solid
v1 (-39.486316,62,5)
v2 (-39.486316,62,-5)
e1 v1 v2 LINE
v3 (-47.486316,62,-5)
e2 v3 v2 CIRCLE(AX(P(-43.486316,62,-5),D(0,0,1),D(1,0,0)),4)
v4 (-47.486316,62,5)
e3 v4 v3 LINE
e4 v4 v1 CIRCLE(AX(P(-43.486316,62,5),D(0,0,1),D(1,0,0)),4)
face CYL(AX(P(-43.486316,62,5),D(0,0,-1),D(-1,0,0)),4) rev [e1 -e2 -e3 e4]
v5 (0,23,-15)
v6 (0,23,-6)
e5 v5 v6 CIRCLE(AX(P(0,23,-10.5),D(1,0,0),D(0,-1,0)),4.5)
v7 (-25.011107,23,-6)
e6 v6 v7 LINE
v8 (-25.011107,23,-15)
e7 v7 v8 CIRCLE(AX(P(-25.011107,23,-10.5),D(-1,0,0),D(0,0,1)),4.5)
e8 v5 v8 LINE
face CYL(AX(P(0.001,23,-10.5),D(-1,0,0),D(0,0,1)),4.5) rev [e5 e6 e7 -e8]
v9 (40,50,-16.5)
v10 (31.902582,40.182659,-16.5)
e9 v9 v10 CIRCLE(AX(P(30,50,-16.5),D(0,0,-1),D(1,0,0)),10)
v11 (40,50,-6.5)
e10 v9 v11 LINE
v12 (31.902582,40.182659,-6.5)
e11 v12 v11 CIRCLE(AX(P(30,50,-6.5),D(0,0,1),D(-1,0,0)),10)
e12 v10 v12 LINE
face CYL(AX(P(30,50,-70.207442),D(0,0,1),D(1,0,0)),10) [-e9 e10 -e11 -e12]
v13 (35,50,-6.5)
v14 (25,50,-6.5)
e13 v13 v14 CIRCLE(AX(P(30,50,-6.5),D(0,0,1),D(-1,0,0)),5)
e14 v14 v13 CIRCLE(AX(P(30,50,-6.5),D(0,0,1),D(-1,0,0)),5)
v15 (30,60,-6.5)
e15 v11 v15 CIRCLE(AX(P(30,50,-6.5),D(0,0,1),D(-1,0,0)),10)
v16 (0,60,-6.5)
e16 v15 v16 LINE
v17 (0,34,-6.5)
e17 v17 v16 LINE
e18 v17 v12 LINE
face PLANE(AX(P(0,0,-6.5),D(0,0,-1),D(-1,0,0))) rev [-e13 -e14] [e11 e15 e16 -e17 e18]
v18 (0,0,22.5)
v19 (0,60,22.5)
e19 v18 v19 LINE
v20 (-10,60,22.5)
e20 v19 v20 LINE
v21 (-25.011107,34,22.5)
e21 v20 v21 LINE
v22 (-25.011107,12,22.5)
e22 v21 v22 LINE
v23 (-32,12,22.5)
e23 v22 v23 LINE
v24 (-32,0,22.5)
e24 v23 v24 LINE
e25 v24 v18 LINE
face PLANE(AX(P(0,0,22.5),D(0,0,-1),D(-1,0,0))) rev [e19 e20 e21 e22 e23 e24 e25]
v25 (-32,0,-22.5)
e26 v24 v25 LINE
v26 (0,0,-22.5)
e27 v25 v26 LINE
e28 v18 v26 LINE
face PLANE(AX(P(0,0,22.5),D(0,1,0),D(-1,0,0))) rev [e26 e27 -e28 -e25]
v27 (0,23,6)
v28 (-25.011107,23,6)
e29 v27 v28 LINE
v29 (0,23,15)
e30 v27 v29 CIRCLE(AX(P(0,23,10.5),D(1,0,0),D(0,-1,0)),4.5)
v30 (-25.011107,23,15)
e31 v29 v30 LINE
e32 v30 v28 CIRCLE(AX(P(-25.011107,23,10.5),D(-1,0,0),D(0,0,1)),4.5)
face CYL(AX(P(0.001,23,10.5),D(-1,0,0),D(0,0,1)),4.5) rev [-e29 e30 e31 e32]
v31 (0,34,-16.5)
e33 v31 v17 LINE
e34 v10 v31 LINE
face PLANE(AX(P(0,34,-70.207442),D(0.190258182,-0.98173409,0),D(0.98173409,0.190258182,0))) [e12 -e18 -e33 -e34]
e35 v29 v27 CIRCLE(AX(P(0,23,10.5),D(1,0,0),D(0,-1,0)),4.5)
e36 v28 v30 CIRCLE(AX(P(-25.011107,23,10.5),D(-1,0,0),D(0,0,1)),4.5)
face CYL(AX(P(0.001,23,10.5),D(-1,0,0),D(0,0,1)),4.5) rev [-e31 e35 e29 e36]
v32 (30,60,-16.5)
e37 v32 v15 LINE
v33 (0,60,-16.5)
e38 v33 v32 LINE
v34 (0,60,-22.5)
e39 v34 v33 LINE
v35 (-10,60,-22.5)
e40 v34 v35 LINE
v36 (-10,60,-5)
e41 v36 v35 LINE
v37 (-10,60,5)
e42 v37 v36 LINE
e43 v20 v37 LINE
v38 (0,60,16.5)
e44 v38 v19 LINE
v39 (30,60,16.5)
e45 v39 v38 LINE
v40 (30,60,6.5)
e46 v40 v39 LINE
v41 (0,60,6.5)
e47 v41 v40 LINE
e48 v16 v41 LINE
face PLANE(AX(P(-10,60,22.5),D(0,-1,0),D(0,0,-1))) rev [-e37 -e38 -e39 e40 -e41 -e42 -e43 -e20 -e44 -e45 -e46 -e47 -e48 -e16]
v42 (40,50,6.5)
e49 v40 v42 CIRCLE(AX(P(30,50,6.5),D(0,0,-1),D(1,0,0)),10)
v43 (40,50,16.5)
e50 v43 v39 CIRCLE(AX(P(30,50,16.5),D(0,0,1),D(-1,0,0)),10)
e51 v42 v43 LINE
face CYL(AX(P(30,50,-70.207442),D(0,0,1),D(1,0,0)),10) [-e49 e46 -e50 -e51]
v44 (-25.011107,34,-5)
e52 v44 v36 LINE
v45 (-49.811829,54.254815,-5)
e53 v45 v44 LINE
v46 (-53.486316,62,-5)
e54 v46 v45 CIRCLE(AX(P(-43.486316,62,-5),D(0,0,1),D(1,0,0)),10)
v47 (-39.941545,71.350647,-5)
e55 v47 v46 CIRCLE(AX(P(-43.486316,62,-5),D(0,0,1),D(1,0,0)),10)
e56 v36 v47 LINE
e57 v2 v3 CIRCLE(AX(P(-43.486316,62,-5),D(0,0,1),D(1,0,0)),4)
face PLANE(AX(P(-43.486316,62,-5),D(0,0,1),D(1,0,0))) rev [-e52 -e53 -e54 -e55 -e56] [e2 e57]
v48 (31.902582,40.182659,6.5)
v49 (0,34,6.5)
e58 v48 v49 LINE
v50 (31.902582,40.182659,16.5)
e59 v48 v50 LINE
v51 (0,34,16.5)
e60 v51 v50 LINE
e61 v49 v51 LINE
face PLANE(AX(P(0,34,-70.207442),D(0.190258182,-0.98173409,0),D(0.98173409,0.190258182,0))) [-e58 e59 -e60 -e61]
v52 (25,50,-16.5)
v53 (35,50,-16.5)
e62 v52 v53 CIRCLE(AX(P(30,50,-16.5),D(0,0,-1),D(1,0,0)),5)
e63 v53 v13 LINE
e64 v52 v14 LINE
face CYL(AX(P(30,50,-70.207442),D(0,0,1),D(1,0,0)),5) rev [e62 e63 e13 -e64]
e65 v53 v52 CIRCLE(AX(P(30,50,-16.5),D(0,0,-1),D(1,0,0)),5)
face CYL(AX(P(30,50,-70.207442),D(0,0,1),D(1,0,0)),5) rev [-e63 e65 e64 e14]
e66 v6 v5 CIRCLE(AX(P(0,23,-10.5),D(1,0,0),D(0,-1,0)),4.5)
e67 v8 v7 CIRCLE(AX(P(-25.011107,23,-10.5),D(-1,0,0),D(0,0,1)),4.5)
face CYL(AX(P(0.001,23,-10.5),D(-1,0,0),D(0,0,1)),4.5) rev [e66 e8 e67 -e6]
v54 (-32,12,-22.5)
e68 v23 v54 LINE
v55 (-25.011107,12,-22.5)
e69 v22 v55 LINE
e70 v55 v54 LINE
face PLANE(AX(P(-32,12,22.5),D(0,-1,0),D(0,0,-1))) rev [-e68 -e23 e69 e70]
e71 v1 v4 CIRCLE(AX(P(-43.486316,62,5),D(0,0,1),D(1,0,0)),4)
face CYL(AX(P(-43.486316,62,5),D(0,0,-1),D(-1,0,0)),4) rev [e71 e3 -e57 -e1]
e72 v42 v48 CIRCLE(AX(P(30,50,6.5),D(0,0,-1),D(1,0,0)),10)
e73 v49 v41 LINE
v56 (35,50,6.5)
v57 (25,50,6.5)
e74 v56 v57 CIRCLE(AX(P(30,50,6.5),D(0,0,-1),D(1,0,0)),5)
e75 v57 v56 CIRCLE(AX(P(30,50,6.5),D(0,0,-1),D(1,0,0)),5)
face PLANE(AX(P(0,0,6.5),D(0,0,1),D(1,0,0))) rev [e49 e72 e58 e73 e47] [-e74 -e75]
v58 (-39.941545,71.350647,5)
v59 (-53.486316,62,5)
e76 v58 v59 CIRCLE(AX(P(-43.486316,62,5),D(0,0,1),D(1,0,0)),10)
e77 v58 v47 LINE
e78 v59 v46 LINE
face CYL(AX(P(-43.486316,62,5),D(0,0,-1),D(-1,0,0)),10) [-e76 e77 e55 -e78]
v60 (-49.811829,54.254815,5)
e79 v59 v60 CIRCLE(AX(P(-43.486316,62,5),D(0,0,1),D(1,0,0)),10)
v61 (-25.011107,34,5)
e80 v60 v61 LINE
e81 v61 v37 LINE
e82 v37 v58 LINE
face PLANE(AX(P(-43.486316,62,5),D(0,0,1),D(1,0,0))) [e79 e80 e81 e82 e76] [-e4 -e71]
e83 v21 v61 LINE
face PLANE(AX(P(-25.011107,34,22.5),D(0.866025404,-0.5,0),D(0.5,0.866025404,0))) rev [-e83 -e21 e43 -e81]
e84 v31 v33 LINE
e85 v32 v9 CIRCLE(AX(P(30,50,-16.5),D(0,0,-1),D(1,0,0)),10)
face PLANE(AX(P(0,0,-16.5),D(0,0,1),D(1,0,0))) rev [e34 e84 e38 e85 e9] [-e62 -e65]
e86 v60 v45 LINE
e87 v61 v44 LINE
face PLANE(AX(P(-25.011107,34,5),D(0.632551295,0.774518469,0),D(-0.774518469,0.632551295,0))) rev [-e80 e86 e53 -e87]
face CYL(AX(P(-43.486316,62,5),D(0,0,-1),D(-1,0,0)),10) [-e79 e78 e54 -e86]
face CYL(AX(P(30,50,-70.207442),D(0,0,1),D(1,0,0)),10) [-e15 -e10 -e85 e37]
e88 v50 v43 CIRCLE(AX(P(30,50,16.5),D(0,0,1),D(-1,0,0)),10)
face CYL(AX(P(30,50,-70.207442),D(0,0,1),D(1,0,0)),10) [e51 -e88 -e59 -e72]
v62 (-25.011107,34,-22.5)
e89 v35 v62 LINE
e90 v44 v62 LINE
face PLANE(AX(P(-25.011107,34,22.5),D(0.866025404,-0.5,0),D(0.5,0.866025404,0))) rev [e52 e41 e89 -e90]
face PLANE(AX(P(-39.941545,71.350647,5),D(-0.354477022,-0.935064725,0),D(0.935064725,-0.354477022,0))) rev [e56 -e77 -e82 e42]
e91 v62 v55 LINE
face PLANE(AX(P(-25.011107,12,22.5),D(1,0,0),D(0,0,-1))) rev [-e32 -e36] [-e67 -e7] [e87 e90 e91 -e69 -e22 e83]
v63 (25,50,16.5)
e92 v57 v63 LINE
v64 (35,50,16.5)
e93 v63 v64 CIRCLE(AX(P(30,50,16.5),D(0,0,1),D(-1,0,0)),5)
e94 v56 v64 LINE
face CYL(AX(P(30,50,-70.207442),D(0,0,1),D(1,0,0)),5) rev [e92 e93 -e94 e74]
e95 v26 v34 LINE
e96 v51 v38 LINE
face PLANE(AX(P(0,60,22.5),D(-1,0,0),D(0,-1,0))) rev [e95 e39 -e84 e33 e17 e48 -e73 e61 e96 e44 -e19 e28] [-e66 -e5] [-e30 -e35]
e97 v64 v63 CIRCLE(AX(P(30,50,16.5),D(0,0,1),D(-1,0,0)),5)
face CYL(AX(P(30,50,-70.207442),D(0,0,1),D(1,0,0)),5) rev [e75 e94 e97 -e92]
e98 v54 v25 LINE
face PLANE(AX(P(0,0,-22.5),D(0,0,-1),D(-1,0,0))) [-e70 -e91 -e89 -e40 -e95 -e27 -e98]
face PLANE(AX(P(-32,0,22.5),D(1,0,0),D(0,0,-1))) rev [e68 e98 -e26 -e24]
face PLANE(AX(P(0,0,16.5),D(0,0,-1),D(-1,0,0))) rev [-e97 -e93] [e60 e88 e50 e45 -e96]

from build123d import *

# Parameters (mm, degrees)
BASE_BLOCK_DEPTH           = 22.5
LUG_ARM_SKETCH_R           = 4
LUG_ARM_DEPTH              = 5
SIDE_HOLE_9_REACH          = 82.629
SIDE_HOLE_SKETCH_R         = 4.5
CLEVIS_FORK_SKETCH_R       = 5
CLEVIS_FORK_DEPTH          = 45
CLEVIS_PIN_HOLE_SKETCH_W   = 40
CLEVIS_PIN_HOLE_SKETCH_H   = 6
CLEVIS_PIN_HOLE_SKETCH_H_2 = 13
CLEVIS_PIN_HOLES_6_DEPTH   = 84.468772351


with BuildPart() as part:
    # Base Block Profile Sketch → Base Block (new, symmetric)
    with BuildSketch(Plane.XY):
        Polygon((0, 0), (-32, 0), (-32, 12), (-25.011106999, 12), (-25.011106999, 34), (-10, 60), (0, 60), align=None)
    extrude(amount=BASE_BLOCK_DEPTH, both=True)

    # Lug Arm Sketch → Lug Arm (add, symmetric)
    with BuildSketch(Plane.XY):
        with BuildLine():
            Line((-25.011106999, 34), (-49.811828564, 54.254815308))
            ThreePointArc((-49.811828564, 54.254815308), (-52.146569651, 67), (-39.941545389, 71.350647253))
            Line((-39.941545389, 71.350647253), (-10, 60))
            Line((-10, 60), (-25.011106999, 34))
        make_face()
        with Locations((-43.486315613, 62)):
            Circle(LUG_ARM_SKETCH_R, mode=Mode.SUBTRACT)
    extrude(amount=LUG_ARM_DEPTH, both=True)

    # Side Hole Sketch → Side Hole Ø9 (cut, up to next)
    with BuildSketch(Plane.ZY.offset(25.011106999), mode=Mode.PRIVATE) as side_hole_9_sk1:
        with Locations((10.5, 23)):
            Circle(SIDE_HOLE_SKETCH_R)
    side_hole_9_tool1 = extrude(side_hole_9_sk1.sketch, amount=-SIDE_HOLE_9_REACH, mode=Mode.PRIVATE) & part.part
    # Side Hole Sketch → Side Hole Ø9 (cut, up to next)
    with BuildSketch(Plane.ZY.offset(25.011106999), mode=Mode.PRIVATE) as side_hole_9_sk2:
        with Locations((-10.5, 23)):
            Circle(SIDE_HOLE_SKETCH_R)
    side_hole_9_tool2 = extrude(side_hole_9_sk2.sketch, amount=-SIDE_HOLE_9_REACH, mode=Mode.PRIVATE) & part.part
    add(side_hole_9_tool1.solids().sort_by_distance((-25.011107, 23, 10.5))[0], mode=Mode.SUBTRACT)
    add(side_hole_9_tool2.solids().sort_by_distance((-25.011107, 23, -10.5))[0], mode=Mode.SUBTRACT)

    # Clevis Fork Sketch → Clevis Fork (add)
    with BuildSketch(Plane.XY.offset(22.5)):
        with BuildLine():
            Line((0, 60), (30, 60))
            ThreePointArc((30, 60), (39.954230484, 50.95566494), (31.902581816, 40.182659096))
            Line((31.902581816, 40.182659096), (0, 34))
            Line((0, 34), (0, 60))
        make_face()
        with Locations((30, 50)):
            Circle(CLEVIS_FORK_SKETCH_R, mode=Mode.SUBTRACT)
    extrude(amount=-CLEVIS_FORK_DEPTH)

    # Clevis Pin Hole Sketch → Clevis Pin Holes Ø6 (cut, through all)
    with BuildSketch(Plane(origin=(0, 60, 0), x_dir=(1, 0, 0), z_dir=(0, 1, 0))):
        with Locations((20, -19.5)):
            Rectangle(CLEVIS_PIN_HOLE_SKETCH_W, CLEVIS_PIN_HOLE_SKETCH_H)
        with Locations((20, 0)):
            Rectangle(CLEVIS_PIN_HOLE_SKETCH_W, CLEVIS_PIN_HOLE_SKETCH_H_2)
        with Locations((20, 19.5)):
            Rectangle(CLEVIS_PIN_HOLE_SKETCH_W, CLEVIS_PIN_HOLE_SKETCH_H)
    extrude(amount=-CLEVIS_PIN_HOLES_6_DEPTH, mode=Mode.SUBTRACT)


solid = part.part
